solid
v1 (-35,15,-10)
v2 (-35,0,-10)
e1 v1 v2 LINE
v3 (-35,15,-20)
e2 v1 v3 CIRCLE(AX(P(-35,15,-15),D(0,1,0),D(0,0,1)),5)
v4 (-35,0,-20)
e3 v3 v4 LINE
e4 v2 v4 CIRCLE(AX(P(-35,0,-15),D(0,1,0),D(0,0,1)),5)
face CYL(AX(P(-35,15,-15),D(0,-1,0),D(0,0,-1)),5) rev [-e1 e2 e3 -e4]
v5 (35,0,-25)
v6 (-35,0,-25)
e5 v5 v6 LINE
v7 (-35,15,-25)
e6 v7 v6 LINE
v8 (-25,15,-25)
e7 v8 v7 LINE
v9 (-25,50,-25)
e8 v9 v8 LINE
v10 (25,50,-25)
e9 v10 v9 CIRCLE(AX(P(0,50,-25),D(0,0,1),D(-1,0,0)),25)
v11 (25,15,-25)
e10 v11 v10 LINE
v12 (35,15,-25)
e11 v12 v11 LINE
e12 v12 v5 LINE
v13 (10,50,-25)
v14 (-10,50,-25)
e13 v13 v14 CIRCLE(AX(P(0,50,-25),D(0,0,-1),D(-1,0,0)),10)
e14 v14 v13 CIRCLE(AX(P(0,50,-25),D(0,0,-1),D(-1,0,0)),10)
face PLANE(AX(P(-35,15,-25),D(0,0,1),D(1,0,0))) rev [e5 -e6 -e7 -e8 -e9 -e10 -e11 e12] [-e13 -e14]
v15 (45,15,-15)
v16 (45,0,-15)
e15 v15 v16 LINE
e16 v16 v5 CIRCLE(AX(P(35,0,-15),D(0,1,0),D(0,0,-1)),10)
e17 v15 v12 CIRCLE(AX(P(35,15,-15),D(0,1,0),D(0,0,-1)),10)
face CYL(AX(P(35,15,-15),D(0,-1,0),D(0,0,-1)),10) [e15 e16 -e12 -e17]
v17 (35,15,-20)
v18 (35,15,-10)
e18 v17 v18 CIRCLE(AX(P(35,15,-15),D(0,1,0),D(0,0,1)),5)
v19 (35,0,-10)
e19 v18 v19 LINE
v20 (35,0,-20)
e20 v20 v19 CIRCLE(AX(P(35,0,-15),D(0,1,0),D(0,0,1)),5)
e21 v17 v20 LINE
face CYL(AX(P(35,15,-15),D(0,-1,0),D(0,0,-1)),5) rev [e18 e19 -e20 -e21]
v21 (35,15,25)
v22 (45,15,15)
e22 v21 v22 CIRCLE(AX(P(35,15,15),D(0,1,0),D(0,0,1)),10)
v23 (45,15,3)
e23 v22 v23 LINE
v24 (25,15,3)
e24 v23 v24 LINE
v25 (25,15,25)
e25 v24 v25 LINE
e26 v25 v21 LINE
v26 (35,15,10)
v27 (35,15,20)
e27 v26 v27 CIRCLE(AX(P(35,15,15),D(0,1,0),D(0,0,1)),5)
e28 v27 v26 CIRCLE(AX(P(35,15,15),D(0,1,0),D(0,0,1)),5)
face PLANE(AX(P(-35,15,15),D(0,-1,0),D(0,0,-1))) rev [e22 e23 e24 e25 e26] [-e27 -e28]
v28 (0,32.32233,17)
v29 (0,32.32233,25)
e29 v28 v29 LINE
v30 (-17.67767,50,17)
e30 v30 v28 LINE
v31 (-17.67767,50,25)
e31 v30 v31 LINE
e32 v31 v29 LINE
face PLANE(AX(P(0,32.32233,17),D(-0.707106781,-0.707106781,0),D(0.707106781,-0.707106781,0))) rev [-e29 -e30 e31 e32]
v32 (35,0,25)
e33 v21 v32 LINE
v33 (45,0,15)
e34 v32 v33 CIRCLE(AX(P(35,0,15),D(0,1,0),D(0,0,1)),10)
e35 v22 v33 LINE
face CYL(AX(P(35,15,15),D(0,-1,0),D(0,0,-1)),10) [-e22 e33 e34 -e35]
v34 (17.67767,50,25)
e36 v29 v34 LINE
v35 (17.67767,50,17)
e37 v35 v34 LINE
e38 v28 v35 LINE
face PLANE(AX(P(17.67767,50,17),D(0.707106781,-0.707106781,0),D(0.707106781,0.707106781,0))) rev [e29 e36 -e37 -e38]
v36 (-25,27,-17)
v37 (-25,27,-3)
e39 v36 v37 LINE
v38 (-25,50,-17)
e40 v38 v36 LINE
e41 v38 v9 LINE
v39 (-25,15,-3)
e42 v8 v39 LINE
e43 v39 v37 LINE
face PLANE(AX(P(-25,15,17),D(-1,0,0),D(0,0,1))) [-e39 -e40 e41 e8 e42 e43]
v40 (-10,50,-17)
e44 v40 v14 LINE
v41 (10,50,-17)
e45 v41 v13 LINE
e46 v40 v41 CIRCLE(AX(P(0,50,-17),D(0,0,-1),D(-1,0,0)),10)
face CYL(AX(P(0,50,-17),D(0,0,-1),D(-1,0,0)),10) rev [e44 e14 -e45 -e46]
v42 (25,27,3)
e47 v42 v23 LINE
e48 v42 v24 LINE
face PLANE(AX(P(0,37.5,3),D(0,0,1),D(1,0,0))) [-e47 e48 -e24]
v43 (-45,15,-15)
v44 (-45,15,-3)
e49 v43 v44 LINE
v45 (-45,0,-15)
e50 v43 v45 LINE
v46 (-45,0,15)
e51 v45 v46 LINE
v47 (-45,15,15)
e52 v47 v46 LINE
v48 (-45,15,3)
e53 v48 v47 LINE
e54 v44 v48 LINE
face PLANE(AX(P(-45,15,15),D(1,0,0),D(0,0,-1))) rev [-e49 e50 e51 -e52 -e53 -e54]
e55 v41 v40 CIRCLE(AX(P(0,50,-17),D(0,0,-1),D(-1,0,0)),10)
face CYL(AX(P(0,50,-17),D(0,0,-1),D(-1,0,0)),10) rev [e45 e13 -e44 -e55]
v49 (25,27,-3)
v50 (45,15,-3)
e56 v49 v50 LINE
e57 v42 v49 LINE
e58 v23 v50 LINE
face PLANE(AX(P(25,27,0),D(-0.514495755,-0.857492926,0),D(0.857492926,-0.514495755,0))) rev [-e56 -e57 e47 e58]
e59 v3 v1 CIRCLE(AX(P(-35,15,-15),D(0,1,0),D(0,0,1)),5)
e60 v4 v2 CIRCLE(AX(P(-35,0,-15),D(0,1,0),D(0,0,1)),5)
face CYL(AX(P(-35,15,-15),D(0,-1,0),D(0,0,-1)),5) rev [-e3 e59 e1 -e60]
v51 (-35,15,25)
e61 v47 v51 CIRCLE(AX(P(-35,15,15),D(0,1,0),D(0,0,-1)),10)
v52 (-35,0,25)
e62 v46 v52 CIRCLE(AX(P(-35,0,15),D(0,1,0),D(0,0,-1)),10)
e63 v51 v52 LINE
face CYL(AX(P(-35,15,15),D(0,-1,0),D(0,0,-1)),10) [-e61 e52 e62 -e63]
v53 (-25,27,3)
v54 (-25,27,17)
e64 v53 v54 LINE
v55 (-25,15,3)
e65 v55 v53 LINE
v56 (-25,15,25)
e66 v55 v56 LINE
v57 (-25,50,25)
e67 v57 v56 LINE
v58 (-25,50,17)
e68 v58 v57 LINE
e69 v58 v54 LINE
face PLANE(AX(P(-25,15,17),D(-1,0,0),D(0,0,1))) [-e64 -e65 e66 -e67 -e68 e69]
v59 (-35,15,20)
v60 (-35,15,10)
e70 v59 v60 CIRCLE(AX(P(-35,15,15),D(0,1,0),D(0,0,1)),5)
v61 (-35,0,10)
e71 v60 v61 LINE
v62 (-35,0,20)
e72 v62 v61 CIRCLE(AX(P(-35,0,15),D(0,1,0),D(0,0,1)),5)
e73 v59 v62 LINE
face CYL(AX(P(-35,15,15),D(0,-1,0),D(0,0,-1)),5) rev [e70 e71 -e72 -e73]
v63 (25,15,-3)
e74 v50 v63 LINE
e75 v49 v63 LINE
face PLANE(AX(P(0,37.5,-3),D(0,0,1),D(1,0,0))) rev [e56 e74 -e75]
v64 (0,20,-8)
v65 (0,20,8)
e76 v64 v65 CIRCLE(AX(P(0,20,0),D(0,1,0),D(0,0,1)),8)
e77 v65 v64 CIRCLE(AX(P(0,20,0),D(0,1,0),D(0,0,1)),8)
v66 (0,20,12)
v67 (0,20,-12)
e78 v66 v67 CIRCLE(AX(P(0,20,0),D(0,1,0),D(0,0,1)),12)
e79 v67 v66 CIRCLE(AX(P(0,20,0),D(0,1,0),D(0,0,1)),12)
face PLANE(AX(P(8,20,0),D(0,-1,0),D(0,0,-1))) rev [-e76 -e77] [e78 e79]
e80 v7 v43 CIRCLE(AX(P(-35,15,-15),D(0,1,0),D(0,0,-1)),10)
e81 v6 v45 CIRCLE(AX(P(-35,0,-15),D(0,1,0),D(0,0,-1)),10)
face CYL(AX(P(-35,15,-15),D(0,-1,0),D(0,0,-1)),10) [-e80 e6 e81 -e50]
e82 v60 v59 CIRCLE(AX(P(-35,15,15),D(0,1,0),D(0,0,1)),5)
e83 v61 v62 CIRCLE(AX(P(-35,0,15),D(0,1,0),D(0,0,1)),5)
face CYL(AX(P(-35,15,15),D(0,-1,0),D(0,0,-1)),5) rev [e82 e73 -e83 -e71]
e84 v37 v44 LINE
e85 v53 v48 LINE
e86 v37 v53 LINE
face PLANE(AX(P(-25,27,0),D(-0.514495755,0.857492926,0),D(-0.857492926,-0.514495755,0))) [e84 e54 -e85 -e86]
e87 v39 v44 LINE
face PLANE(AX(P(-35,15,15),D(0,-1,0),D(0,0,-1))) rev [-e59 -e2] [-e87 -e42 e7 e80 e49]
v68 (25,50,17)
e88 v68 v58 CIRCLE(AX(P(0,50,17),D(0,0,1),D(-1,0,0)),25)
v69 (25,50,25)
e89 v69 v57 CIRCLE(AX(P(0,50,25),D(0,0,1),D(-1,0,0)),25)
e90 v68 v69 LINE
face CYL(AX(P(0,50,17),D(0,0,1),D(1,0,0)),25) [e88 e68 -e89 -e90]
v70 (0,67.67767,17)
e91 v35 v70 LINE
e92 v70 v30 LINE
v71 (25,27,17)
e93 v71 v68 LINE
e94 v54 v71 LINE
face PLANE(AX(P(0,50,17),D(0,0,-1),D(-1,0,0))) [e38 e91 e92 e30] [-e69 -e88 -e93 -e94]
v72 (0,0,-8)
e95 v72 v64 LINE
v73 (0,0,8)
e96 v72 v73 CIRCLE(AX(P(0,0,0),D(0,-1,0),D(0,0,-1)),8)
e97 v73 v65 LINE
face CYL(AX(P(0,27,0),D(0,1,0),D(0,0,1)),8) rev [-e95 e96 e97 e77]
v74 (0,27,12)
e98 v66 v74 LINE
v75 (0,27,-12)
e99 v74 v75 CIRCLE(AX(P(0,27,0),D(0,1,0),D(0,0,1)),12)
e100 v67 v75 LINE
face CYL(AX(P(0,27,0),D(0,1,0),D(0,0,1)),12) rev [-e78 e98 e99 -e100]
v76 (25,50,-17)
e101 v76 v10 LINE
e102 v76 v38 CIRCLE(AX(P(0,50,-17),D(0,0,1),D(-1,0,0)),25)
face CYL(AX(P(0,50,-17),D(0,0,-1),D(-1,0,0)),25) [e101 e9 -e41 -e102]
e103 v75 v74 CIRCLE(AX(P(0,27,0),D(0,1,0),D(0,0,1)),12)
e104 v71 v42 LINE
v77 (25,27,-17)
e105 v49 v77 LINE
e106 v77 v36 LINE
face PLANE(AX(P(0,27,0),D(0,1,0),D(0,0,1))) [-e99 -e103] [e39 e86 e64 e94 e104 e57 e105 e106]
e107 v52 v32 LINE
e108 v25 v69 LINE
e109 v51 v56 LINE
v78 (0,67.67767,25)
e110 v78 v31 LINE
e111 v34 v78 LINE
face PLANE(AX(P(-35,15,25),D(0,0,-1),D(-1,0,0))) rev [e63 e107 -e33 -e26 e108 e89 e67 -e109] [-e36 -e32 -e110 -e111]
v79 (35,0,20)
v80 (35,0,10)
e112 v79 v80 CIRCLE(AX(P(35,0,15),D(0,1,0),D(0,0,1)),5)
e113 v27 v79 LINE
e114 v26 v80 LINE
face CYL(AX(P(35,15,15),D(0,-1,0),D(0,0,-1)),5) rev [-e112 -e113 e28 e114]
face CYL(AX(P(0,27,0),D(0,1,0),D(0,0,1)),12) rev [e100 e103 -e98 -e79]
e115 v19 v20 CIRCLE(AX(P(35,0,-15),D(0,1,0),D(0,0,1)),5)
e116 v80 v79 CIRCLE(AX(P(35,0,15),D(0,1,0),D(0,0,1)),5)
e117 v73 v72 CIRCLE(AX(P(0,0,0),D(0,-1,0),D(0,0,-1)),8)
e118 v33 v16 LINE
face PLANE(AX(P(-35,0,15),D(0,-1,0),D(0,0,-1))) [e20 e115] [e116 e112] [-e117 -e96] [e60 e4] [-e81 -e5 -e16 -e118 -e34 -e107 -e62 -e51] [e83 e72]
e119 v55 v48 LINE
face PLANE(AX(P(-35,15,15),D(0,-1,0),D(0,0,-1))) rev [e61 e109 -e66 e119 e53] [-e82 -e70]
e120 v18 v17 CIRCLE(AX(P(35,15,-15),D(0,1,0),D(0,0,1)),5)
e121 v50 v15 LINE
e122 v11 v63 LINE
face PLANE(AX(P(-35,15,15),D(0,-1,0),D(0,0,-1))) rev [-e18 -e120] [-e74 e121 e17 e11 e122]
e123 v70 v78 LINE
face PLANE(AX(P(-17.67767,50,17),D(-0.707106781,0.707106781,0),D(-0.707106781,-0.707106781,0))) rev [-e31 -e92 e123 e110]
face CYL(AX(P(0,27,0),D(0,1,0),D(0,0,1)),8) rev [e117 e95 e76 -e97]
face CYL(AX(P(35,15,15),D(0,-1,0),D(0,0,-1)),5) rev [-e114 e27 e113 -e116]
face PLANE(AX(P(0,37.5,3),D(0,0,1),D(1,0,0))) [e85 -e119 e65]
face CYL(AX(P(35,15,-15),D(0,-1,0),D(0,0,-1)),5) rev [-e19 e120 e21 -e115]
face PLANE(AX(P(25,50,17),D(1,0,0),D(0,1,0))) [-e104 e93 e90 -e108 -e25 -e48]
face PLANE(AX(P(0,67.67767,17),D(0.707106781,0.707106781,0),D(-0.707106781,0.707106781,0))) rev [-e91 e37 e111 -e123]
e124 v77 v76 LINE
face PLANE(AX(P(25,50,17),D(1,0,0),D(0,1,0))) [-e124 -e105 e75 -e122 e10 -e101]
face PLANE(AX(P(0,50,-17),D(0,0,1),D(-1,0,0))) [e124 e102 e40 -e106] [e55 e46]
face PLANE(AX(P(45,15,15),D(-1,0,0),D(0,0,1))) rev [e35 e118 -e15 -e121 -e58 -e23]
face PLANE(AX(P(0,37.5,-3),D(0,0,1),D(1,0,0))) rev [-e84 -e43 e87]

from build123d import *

# Parameters (mm, degrees)
BASE_PLATE_SKETCH_R              = 5
BASE_PLATE_DEPTH                 = 15
CLEVIS_EAR_DEPTH                 = 8
CENTRE_CUT_DEPTH                 = 8
PIN_BORE_SKETCH_R                = 10
PIN_BORE_20_DEPTH                = 8
EAR_BOSS_SKETCH_W                = 50
EAR_BOSS_SKETCH_H                = 34
EAR_BOSS_DEPTH                   = 12
GUSSET_RIB_REACH                 = 92.967
GUSSET_SKETCH_WALL_W             = 207.257861566
GUSSET_SKETCH_WALL_H             = 6
COUNTERBORED_HOLE_16_D           = 16
COUNTERBORED_HOLE_16_DEPTH       = 49.839743178
COUNTERBORED_HOLE_16_CBORE_D     = 24
COUNTERBORED_HOLE_16_CBORE_DEPTH = 7


with BuildPart() as part:
    # Base Plate Sketch → Base Plate (new body)
    with BuildSketch(Plane(origin=(0, 0, 0), x_dir=(1, 0, 0), z_dir=(0, 1, 0))):
        with BuildLine():
            Line((-35, -25), (35, -25))
            ThreePointArc((35, -25), (42.071067812, -22.071067812), (45, -15))
            Line((45, -15), (45, 15))
            ThreePointArc((45, 15), (42.071067812, 22.071067812), (35, 25))
            Line((35, 25), (-35, 25))
            ThreePointArc((-35, 25), (-42.071067812, 22.071067812), (-45, 15))
            Line((-45, 15), (-45, -15))
            ThreePointArc((-45, -15), (-42.071067812, -22.071067812), (-35, -25))
        make_face()
        with Locations(Location((-35, 15, 0), (0, 0, 270))):
            Circle(BASE_PLATE_SKETCH_R, mode=Mode.SUBTRACT)
        with Locations(Location((35, 15, 0), (0, 0, 270))):
            Circle(BASE_PLATE_SKETCH_R, mode=Mode.SUBTRACT)
        with Locations(Location((-35, -15, 0), (0, 0, 270))):
            Circle(BASE_PLATE_SKETCH_R, mode=Mode.SUBTRACT)
        with Locations(Location((35, -15, 0), (0, 0, 270))):
            Circle(BASE_PLATE_SKETCH_R, mode=Mode.SUBTRACT)
    extrude(amount=BASE_PLATE_DEPTH)

    # Clevis Ear Sketch → Clevis Ear (add)
    with BuildSketch(Plane.XY.offset(25)):
        with BuildLine():
            Line((-25, 15), (-25, 50))
            ThreePointArc((-25, 50), (0, 75), (25, 50))
            Line((25, 50), (25, 15))
            Line((25, 15), (-25, 15))
        make_face()
    clevis_ear = extrude(amount=-CLEVIS_EAR_DEPTH)

    # Clevis Ear Mirror: Clevis Ear across plane
    add(clevis_ear.mirror(Plane.XY))

    # Centre Cut Sketch → Centre Cut (cut)
    with BuildSketch(Plane.XY.offset(25)):
        Polygon((-17.67766953, 50), (0, 67.67766953), (17.67766953, 50), (0, 32.32233047), align=None)
    extrude(amount=-CENTRE_CUT_DEPTH, mode=Mode.SUBTRACT)

    # Pin Bore Sketch → Pin Bore Ø20 (cut)
    with BuildSketch(Plane(origin=(0, 0, -25), x_dir=(-1, 0, 0), z_dir=(0, 0, -1))):
        with Locations((0, 50)):
            Circle(PIN_BORE_SKETCH_R)
    extrude(amount=-PIN_BORE_20_DEPTH, mode=Mode.SUBTRACT)

    # Ear Boss Sketch → Ear Boss (add)
    with BuildSketch(Plane(origin=(0, 15, 0), x_dir=(1, 0, 0), z_dir=(0, 1, 0))):
        Rectangle(EAR_BOSS_SKETCH_W, EAR_BOSS_SKETCH_H)
    extrude(amount=EAR_BOSS_DEPTH)

    # Gusset Sketch wall → Gusset Rib (add, up to next)
    with BuildSketch(Plane(origin=(35, 21, 0), x_dir=(0.857492925713, -0.514495755428, 0), z_dir=(0.514495755428, 0.857492925713, 0)), mode=Mode.PRIVATE) as gusset_rib_sk1:
        Rectangle(GUSSET_SKETCH_WALL_W, GUSSET_SKETCH_WALL_H)
    gusset_rib_tool1 = extrude(gusset_rib_sk1.sketch, amount=-GUSSET_RIB_REACH, mode=Mode.PRIVATE) - part.part
    gusset_rib = gusset_rib_tool1.solids().sort_by_distance((35, 21, 0))[0]
    add(gusset_rib)

    # Gusset Rib Mirror: Gusset Rib across plane
    add(gusset_rib.mirror(Plane(origin=(0, 0, 0), x_dir=(0, 0, 1), z_dir=(1, 0, 0))))

    # Counterbored Hole Ø16
    with Locations(Plane.ZX.offset(27)):
        with Locations((0, 0)):
            CounterBoreHole(COUNTERBORED_HOLE_16_D / 2, COUNTERBORED_HOLE_16_CBORE_D / 2, COUNTERBORED_HOLE_16_CBORE_DEPTH, depth=COUNTERBORED_HOLE_16_DEPTH)


solid = part.part
